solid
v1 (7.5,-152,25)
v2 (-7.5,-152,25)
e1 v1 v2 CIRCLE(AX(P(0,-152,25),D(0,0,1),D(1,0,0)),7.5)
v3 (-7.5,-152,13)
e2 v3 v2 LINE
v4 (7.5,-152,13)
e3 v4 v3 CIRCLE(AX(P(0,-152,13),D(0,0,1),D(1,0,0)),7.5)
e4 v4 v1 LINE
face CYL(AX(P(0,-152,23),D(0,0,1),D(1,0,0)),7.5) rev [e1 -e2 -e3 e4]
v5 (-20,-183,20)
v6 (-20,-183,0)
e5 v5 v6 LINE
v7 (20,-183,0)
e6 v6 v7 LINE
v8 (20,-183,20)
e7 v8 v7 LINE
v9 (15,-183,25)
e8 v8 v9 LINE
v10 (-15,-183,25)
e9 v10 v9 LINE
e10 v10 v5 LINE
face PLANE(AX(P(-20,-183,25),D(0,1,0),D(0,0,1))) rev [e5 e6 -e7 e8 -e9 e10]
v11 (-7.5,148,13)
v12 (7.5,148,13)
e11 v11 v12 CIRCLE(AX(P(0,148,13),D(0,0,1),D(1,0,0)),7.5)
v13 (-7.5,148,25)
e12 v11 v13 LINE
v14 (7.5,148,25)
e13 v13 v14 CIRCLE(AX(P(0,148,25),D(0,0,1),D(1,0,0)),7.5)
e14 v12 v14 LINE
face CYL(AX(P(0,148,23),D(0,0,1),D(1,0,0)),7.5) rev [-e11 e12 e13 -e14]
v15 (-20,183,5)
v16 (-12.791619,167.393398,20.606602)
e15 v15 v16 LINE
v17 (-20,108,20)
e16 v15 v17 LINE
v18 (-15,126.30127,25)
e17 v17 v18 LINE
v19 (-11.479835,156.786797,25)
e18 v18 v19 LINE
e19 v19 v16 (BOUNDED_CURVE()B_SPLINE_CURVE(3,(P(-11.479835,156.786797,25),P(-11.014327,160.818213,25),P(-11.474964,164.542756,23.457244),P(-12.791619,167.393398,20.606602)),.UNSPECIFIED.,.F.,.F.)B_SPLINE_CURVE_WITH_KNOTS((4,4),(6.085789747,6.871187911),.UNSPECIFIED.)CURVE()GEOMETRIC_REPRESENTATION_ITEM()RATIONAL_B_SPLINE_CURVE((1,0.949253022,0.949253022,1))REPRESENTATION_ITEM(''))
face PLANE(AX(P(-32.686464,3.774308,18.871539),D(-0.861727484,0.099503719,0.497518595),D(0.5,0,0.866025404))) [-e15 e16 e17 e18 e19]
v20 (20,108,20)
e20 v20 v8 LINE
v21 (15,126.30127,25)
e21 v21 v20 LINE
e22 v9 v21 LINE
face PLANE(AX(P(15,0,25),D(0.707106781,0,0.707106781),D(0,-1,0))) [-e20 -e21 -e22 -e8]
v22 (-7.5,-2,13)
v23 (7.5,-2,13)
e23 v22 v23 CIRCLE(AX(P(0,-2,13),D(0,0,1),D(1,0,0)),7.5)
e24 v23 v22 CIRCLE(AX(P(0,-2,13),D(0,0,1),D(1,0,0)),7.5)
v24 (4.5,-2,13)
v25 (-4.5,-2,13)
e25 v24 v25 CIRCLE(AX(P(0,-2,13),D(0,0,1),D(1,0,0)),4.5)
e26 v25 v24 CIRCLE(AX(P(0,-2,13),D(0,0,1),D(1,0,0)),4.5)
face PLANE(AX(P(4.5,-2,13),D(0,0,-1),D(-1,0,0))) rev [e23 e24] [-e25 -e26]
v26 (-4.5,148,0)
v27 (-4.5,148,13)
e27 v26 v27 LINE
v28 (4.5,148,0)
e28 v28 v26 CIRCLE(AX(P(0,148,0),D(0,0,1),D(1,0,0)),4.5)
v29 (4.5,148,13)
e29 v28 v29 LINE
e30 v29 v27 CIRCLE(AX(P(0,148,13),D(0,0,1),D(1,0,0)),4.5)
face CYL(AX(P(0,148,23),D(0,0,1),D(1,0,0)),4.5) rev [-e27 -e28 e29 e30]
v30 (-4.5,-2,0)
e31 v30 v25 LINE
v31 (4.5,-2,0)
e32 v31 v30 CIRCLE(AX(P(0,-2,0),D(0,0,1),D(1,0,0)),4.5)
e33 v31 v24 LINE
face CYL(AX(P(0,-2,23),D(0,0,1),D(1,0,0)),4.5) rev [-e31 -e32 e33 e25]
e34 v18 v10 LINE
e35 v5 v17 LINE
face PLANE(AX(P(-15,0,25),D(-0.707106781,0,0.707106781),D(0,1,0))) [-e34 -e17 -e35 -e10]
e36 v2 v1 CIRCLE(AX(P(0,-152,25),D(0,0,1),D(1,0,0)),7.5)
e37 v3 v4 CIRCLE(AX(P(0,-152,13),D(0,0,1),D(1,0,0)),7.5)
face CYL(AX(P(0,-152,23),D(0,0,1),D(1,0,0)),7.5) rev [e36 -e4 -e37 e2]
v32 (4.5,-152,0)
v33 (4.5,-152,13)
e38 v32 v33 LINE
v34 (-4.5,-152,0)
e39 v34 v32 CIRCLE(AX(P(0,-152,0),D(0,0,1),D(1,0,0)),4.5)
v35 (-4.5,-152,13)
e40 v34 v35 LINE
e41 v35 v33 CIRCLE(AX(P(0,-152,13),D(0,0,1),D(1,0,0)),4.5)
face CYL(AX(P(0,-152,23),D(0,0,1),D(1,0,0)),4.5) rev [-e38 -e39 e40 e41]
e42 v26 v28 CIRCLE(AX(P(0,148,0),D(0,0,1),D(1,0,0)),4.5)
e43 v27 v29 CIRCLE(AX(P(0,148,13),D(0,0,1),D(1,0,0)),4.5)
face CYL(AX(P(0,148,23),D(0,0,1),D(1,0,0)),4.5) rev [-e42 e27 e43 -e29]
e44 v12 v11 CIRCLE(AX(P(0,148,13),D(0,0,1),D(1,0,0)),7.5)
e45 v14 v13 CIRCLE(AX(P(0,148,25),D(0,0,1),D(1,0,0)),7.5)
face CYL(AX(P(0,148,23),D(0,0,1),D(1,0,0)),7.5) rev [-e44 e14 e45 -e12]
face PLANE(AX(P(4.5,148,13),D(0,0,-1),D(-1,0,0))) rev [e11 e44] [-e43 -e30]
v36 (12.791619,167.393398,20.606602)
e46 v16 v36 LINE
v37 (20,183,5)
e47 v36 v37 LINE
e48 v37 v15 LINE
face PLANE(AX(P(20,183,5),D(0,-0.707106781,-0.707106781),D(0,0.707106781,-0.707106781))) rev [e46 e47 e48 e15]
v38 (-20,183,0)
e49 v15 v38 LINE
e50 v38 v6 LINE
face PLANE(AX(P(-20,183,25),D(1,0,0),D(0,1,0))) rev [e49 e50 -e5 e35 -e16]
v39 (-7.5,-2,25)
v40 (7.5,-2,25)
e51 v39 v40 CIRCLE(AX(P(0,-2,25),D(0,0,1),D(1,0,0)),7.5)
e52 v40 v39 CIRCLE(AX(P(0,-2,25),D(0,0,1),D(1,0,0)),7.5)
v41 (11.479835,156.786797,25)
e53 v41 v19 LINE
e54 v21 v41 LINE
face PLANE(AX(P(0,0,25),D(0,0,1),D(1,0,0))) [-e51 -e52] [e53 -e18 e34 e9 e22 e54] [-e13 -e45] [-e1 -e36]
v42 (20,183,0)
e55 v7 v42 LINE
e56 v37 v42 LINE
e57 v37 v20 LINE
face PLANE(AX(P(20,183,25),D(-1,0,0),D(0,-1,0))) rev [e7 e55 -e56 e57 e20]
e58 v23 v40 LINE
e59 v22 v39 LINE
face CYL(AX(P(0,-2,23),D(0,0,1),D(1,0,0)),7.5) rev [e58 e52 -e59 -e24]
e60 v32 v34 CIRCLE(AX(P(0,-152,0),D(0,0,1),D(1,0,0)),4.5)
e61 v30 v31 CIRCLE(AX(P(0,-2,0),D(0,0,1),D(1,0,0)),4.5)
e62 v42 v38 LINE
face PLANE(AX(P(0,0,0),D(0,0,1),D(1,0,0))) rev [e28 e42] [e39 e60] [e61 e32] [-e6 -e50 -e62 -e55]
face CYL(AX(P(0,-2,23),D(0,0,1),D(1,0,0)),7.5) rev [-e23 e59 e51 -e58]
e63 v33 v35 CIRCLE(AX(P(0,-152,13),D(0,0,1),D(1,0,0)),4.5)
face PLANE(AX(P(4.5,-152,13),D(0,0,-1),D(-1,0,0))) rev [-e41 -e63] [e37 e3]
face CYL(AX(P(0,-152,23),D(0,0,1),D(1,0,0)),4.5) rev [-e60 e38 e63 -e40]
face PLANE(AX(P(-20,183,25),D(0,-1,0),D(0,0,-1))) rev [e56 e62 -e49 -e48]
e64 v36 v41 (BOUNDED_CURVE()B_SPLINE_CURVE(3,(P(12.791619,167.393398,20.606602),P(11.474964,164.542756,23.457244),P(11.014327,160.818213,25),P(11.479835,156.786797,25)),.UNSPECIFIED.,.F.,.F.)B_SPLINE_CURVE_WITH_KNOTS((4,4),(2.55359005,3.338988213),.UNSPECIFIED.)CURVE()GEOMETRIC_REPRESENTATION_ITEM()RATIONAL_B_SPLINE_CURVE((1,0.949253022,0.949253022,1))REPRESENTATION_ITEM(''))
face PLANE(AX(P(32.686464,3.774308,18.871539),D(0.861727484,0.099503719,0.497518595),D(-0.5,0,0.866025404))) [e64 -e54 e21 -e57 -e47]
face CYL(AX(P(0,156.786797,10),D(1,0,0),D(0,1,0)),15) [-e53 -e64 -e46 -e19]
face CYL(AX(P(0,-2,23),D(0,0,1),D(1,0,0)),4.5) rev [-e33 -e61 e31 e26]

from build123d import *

# Parameters (mm, degrees)
SKETCH1_W                                          = 40
SKETCH1_H                                          = 366
BOSS_EXTRUDE1_DEPTH                                = 25
SKETCH4_R                                          = 7.5
CUT_EXTRUDE1_DEPTH                                 = 2
HOLE_SIZE_BASED_ON_HEX_SOCKET_CAP_SCRE_D           = 9
HOLE_SIZE_BASED_ON_HEX_SOCKET_CAP_SCRE_CBORE_D     = 15
HOLE_SIZE_BASED_ON_HEX_SOCKET_CAP_SCRE_CBORE_DEPTH = 10
CUT_EXTRUDE4_DEPTH                                 = 15
CHAMFER4_SIZE                                      = 5
CUT_EXTRUDE5_DEPTH                                 = 189.981480574
FILLET3_R                                          = 15


with BuildPart() as part:
    # Sketch1 → Boss-Extrude1 (new body)
    with BuildSketch(Plane.XY):
        Rectangle(SKETCH1_W, SKETCH1_H)
    extrude(amount=BOSS_EXTRUDE1_DEPTH)

    # Sketch4 → Cut-Extrude1 (cut)
    with BuildSketch(Plane.XY.offset(25)):
        with Locations((0, -152)):
            Circle(SKETCH4_R)
        with Locations((0, -2)):
            Circle(SKETCH4_R)
        with Locations((0, 148)):
            Circle(SKETCH4_R)
    extrude(amount=-CUT_EXTRUDE1_DEPTH, mode=Mode.SUBTRACT)

    # Hole Size (based on) hex socket cap screw type 1 (through all)
    with Locations(Plane.XY.offset(23)):
        with Locations((0, -152), (0, -2), (0, 148)):
            CounterBoreHole(HOLE_SIZE_BASED_ON_HEX_SOCKET_CAP_SCRE_D / 2, HOLE_SIZE_BASED_ON_HEX_SOCKET_CAP_SCRE_CBORE_D / 2, HOLE_SIZE_BASED_ON_HEX_SOCKET_CAP_SCRE_CBORE_DEPTH)

    # Sketch13 → Cut-Extrude4 (cut)
    with BuildSketch(Plane(origin=(-32.686463761, 3.77430773, 18.871538651), x_dir=(0.46855304860894914, -0.22010109077968257, 0.855577904387937), z_dir=(-0.8617274844321422, 0.09950371902099794, 0.49751859510498975))):
        Polygon((-6.250003897, 80.225632862), (-22.8497284, 179.511998894), (-45.371671063, 174.403630071), align=None)
    cut_extrude4 = extrude(amount=CUT_EXTRUDE4_DEPTH, mode=Mode.SUBTRACT)

    # Mirror1: Cut-Extrude4 across plane
    add(cut_extrude4.mirror(Plane.ZY), mode=Mode.SUBTRACT)

    # Chamfer4
    chamfer4_edges = [part.edges().sort_by_distance(p)[0] for p in [
        (-20, -50, 25),
        (20, -50, 25),
    ]]
    chamfer(chamfer4_edges, length=CHAMFER4_SIZE)

    # Sketch14 → Cut-Extrude5 (cut, through all)
    with BuildSketch(Plane.ZY.offset(20)):
        Polygon((5, 183), (25, 163), (25, 183), align=None)
    extrude(amount=-CUT_EXTRUDE5_DEPTH, mode=Mode.SUBTRACT)

    # Fillet3
    fillet3_edges = [part.edges().sort_by_distance(p)[0] for p in [
        (0, 163, 25),
    ]]
    fillet(fillet3_edges, radius=FILLET3_R)


solid = part.part
